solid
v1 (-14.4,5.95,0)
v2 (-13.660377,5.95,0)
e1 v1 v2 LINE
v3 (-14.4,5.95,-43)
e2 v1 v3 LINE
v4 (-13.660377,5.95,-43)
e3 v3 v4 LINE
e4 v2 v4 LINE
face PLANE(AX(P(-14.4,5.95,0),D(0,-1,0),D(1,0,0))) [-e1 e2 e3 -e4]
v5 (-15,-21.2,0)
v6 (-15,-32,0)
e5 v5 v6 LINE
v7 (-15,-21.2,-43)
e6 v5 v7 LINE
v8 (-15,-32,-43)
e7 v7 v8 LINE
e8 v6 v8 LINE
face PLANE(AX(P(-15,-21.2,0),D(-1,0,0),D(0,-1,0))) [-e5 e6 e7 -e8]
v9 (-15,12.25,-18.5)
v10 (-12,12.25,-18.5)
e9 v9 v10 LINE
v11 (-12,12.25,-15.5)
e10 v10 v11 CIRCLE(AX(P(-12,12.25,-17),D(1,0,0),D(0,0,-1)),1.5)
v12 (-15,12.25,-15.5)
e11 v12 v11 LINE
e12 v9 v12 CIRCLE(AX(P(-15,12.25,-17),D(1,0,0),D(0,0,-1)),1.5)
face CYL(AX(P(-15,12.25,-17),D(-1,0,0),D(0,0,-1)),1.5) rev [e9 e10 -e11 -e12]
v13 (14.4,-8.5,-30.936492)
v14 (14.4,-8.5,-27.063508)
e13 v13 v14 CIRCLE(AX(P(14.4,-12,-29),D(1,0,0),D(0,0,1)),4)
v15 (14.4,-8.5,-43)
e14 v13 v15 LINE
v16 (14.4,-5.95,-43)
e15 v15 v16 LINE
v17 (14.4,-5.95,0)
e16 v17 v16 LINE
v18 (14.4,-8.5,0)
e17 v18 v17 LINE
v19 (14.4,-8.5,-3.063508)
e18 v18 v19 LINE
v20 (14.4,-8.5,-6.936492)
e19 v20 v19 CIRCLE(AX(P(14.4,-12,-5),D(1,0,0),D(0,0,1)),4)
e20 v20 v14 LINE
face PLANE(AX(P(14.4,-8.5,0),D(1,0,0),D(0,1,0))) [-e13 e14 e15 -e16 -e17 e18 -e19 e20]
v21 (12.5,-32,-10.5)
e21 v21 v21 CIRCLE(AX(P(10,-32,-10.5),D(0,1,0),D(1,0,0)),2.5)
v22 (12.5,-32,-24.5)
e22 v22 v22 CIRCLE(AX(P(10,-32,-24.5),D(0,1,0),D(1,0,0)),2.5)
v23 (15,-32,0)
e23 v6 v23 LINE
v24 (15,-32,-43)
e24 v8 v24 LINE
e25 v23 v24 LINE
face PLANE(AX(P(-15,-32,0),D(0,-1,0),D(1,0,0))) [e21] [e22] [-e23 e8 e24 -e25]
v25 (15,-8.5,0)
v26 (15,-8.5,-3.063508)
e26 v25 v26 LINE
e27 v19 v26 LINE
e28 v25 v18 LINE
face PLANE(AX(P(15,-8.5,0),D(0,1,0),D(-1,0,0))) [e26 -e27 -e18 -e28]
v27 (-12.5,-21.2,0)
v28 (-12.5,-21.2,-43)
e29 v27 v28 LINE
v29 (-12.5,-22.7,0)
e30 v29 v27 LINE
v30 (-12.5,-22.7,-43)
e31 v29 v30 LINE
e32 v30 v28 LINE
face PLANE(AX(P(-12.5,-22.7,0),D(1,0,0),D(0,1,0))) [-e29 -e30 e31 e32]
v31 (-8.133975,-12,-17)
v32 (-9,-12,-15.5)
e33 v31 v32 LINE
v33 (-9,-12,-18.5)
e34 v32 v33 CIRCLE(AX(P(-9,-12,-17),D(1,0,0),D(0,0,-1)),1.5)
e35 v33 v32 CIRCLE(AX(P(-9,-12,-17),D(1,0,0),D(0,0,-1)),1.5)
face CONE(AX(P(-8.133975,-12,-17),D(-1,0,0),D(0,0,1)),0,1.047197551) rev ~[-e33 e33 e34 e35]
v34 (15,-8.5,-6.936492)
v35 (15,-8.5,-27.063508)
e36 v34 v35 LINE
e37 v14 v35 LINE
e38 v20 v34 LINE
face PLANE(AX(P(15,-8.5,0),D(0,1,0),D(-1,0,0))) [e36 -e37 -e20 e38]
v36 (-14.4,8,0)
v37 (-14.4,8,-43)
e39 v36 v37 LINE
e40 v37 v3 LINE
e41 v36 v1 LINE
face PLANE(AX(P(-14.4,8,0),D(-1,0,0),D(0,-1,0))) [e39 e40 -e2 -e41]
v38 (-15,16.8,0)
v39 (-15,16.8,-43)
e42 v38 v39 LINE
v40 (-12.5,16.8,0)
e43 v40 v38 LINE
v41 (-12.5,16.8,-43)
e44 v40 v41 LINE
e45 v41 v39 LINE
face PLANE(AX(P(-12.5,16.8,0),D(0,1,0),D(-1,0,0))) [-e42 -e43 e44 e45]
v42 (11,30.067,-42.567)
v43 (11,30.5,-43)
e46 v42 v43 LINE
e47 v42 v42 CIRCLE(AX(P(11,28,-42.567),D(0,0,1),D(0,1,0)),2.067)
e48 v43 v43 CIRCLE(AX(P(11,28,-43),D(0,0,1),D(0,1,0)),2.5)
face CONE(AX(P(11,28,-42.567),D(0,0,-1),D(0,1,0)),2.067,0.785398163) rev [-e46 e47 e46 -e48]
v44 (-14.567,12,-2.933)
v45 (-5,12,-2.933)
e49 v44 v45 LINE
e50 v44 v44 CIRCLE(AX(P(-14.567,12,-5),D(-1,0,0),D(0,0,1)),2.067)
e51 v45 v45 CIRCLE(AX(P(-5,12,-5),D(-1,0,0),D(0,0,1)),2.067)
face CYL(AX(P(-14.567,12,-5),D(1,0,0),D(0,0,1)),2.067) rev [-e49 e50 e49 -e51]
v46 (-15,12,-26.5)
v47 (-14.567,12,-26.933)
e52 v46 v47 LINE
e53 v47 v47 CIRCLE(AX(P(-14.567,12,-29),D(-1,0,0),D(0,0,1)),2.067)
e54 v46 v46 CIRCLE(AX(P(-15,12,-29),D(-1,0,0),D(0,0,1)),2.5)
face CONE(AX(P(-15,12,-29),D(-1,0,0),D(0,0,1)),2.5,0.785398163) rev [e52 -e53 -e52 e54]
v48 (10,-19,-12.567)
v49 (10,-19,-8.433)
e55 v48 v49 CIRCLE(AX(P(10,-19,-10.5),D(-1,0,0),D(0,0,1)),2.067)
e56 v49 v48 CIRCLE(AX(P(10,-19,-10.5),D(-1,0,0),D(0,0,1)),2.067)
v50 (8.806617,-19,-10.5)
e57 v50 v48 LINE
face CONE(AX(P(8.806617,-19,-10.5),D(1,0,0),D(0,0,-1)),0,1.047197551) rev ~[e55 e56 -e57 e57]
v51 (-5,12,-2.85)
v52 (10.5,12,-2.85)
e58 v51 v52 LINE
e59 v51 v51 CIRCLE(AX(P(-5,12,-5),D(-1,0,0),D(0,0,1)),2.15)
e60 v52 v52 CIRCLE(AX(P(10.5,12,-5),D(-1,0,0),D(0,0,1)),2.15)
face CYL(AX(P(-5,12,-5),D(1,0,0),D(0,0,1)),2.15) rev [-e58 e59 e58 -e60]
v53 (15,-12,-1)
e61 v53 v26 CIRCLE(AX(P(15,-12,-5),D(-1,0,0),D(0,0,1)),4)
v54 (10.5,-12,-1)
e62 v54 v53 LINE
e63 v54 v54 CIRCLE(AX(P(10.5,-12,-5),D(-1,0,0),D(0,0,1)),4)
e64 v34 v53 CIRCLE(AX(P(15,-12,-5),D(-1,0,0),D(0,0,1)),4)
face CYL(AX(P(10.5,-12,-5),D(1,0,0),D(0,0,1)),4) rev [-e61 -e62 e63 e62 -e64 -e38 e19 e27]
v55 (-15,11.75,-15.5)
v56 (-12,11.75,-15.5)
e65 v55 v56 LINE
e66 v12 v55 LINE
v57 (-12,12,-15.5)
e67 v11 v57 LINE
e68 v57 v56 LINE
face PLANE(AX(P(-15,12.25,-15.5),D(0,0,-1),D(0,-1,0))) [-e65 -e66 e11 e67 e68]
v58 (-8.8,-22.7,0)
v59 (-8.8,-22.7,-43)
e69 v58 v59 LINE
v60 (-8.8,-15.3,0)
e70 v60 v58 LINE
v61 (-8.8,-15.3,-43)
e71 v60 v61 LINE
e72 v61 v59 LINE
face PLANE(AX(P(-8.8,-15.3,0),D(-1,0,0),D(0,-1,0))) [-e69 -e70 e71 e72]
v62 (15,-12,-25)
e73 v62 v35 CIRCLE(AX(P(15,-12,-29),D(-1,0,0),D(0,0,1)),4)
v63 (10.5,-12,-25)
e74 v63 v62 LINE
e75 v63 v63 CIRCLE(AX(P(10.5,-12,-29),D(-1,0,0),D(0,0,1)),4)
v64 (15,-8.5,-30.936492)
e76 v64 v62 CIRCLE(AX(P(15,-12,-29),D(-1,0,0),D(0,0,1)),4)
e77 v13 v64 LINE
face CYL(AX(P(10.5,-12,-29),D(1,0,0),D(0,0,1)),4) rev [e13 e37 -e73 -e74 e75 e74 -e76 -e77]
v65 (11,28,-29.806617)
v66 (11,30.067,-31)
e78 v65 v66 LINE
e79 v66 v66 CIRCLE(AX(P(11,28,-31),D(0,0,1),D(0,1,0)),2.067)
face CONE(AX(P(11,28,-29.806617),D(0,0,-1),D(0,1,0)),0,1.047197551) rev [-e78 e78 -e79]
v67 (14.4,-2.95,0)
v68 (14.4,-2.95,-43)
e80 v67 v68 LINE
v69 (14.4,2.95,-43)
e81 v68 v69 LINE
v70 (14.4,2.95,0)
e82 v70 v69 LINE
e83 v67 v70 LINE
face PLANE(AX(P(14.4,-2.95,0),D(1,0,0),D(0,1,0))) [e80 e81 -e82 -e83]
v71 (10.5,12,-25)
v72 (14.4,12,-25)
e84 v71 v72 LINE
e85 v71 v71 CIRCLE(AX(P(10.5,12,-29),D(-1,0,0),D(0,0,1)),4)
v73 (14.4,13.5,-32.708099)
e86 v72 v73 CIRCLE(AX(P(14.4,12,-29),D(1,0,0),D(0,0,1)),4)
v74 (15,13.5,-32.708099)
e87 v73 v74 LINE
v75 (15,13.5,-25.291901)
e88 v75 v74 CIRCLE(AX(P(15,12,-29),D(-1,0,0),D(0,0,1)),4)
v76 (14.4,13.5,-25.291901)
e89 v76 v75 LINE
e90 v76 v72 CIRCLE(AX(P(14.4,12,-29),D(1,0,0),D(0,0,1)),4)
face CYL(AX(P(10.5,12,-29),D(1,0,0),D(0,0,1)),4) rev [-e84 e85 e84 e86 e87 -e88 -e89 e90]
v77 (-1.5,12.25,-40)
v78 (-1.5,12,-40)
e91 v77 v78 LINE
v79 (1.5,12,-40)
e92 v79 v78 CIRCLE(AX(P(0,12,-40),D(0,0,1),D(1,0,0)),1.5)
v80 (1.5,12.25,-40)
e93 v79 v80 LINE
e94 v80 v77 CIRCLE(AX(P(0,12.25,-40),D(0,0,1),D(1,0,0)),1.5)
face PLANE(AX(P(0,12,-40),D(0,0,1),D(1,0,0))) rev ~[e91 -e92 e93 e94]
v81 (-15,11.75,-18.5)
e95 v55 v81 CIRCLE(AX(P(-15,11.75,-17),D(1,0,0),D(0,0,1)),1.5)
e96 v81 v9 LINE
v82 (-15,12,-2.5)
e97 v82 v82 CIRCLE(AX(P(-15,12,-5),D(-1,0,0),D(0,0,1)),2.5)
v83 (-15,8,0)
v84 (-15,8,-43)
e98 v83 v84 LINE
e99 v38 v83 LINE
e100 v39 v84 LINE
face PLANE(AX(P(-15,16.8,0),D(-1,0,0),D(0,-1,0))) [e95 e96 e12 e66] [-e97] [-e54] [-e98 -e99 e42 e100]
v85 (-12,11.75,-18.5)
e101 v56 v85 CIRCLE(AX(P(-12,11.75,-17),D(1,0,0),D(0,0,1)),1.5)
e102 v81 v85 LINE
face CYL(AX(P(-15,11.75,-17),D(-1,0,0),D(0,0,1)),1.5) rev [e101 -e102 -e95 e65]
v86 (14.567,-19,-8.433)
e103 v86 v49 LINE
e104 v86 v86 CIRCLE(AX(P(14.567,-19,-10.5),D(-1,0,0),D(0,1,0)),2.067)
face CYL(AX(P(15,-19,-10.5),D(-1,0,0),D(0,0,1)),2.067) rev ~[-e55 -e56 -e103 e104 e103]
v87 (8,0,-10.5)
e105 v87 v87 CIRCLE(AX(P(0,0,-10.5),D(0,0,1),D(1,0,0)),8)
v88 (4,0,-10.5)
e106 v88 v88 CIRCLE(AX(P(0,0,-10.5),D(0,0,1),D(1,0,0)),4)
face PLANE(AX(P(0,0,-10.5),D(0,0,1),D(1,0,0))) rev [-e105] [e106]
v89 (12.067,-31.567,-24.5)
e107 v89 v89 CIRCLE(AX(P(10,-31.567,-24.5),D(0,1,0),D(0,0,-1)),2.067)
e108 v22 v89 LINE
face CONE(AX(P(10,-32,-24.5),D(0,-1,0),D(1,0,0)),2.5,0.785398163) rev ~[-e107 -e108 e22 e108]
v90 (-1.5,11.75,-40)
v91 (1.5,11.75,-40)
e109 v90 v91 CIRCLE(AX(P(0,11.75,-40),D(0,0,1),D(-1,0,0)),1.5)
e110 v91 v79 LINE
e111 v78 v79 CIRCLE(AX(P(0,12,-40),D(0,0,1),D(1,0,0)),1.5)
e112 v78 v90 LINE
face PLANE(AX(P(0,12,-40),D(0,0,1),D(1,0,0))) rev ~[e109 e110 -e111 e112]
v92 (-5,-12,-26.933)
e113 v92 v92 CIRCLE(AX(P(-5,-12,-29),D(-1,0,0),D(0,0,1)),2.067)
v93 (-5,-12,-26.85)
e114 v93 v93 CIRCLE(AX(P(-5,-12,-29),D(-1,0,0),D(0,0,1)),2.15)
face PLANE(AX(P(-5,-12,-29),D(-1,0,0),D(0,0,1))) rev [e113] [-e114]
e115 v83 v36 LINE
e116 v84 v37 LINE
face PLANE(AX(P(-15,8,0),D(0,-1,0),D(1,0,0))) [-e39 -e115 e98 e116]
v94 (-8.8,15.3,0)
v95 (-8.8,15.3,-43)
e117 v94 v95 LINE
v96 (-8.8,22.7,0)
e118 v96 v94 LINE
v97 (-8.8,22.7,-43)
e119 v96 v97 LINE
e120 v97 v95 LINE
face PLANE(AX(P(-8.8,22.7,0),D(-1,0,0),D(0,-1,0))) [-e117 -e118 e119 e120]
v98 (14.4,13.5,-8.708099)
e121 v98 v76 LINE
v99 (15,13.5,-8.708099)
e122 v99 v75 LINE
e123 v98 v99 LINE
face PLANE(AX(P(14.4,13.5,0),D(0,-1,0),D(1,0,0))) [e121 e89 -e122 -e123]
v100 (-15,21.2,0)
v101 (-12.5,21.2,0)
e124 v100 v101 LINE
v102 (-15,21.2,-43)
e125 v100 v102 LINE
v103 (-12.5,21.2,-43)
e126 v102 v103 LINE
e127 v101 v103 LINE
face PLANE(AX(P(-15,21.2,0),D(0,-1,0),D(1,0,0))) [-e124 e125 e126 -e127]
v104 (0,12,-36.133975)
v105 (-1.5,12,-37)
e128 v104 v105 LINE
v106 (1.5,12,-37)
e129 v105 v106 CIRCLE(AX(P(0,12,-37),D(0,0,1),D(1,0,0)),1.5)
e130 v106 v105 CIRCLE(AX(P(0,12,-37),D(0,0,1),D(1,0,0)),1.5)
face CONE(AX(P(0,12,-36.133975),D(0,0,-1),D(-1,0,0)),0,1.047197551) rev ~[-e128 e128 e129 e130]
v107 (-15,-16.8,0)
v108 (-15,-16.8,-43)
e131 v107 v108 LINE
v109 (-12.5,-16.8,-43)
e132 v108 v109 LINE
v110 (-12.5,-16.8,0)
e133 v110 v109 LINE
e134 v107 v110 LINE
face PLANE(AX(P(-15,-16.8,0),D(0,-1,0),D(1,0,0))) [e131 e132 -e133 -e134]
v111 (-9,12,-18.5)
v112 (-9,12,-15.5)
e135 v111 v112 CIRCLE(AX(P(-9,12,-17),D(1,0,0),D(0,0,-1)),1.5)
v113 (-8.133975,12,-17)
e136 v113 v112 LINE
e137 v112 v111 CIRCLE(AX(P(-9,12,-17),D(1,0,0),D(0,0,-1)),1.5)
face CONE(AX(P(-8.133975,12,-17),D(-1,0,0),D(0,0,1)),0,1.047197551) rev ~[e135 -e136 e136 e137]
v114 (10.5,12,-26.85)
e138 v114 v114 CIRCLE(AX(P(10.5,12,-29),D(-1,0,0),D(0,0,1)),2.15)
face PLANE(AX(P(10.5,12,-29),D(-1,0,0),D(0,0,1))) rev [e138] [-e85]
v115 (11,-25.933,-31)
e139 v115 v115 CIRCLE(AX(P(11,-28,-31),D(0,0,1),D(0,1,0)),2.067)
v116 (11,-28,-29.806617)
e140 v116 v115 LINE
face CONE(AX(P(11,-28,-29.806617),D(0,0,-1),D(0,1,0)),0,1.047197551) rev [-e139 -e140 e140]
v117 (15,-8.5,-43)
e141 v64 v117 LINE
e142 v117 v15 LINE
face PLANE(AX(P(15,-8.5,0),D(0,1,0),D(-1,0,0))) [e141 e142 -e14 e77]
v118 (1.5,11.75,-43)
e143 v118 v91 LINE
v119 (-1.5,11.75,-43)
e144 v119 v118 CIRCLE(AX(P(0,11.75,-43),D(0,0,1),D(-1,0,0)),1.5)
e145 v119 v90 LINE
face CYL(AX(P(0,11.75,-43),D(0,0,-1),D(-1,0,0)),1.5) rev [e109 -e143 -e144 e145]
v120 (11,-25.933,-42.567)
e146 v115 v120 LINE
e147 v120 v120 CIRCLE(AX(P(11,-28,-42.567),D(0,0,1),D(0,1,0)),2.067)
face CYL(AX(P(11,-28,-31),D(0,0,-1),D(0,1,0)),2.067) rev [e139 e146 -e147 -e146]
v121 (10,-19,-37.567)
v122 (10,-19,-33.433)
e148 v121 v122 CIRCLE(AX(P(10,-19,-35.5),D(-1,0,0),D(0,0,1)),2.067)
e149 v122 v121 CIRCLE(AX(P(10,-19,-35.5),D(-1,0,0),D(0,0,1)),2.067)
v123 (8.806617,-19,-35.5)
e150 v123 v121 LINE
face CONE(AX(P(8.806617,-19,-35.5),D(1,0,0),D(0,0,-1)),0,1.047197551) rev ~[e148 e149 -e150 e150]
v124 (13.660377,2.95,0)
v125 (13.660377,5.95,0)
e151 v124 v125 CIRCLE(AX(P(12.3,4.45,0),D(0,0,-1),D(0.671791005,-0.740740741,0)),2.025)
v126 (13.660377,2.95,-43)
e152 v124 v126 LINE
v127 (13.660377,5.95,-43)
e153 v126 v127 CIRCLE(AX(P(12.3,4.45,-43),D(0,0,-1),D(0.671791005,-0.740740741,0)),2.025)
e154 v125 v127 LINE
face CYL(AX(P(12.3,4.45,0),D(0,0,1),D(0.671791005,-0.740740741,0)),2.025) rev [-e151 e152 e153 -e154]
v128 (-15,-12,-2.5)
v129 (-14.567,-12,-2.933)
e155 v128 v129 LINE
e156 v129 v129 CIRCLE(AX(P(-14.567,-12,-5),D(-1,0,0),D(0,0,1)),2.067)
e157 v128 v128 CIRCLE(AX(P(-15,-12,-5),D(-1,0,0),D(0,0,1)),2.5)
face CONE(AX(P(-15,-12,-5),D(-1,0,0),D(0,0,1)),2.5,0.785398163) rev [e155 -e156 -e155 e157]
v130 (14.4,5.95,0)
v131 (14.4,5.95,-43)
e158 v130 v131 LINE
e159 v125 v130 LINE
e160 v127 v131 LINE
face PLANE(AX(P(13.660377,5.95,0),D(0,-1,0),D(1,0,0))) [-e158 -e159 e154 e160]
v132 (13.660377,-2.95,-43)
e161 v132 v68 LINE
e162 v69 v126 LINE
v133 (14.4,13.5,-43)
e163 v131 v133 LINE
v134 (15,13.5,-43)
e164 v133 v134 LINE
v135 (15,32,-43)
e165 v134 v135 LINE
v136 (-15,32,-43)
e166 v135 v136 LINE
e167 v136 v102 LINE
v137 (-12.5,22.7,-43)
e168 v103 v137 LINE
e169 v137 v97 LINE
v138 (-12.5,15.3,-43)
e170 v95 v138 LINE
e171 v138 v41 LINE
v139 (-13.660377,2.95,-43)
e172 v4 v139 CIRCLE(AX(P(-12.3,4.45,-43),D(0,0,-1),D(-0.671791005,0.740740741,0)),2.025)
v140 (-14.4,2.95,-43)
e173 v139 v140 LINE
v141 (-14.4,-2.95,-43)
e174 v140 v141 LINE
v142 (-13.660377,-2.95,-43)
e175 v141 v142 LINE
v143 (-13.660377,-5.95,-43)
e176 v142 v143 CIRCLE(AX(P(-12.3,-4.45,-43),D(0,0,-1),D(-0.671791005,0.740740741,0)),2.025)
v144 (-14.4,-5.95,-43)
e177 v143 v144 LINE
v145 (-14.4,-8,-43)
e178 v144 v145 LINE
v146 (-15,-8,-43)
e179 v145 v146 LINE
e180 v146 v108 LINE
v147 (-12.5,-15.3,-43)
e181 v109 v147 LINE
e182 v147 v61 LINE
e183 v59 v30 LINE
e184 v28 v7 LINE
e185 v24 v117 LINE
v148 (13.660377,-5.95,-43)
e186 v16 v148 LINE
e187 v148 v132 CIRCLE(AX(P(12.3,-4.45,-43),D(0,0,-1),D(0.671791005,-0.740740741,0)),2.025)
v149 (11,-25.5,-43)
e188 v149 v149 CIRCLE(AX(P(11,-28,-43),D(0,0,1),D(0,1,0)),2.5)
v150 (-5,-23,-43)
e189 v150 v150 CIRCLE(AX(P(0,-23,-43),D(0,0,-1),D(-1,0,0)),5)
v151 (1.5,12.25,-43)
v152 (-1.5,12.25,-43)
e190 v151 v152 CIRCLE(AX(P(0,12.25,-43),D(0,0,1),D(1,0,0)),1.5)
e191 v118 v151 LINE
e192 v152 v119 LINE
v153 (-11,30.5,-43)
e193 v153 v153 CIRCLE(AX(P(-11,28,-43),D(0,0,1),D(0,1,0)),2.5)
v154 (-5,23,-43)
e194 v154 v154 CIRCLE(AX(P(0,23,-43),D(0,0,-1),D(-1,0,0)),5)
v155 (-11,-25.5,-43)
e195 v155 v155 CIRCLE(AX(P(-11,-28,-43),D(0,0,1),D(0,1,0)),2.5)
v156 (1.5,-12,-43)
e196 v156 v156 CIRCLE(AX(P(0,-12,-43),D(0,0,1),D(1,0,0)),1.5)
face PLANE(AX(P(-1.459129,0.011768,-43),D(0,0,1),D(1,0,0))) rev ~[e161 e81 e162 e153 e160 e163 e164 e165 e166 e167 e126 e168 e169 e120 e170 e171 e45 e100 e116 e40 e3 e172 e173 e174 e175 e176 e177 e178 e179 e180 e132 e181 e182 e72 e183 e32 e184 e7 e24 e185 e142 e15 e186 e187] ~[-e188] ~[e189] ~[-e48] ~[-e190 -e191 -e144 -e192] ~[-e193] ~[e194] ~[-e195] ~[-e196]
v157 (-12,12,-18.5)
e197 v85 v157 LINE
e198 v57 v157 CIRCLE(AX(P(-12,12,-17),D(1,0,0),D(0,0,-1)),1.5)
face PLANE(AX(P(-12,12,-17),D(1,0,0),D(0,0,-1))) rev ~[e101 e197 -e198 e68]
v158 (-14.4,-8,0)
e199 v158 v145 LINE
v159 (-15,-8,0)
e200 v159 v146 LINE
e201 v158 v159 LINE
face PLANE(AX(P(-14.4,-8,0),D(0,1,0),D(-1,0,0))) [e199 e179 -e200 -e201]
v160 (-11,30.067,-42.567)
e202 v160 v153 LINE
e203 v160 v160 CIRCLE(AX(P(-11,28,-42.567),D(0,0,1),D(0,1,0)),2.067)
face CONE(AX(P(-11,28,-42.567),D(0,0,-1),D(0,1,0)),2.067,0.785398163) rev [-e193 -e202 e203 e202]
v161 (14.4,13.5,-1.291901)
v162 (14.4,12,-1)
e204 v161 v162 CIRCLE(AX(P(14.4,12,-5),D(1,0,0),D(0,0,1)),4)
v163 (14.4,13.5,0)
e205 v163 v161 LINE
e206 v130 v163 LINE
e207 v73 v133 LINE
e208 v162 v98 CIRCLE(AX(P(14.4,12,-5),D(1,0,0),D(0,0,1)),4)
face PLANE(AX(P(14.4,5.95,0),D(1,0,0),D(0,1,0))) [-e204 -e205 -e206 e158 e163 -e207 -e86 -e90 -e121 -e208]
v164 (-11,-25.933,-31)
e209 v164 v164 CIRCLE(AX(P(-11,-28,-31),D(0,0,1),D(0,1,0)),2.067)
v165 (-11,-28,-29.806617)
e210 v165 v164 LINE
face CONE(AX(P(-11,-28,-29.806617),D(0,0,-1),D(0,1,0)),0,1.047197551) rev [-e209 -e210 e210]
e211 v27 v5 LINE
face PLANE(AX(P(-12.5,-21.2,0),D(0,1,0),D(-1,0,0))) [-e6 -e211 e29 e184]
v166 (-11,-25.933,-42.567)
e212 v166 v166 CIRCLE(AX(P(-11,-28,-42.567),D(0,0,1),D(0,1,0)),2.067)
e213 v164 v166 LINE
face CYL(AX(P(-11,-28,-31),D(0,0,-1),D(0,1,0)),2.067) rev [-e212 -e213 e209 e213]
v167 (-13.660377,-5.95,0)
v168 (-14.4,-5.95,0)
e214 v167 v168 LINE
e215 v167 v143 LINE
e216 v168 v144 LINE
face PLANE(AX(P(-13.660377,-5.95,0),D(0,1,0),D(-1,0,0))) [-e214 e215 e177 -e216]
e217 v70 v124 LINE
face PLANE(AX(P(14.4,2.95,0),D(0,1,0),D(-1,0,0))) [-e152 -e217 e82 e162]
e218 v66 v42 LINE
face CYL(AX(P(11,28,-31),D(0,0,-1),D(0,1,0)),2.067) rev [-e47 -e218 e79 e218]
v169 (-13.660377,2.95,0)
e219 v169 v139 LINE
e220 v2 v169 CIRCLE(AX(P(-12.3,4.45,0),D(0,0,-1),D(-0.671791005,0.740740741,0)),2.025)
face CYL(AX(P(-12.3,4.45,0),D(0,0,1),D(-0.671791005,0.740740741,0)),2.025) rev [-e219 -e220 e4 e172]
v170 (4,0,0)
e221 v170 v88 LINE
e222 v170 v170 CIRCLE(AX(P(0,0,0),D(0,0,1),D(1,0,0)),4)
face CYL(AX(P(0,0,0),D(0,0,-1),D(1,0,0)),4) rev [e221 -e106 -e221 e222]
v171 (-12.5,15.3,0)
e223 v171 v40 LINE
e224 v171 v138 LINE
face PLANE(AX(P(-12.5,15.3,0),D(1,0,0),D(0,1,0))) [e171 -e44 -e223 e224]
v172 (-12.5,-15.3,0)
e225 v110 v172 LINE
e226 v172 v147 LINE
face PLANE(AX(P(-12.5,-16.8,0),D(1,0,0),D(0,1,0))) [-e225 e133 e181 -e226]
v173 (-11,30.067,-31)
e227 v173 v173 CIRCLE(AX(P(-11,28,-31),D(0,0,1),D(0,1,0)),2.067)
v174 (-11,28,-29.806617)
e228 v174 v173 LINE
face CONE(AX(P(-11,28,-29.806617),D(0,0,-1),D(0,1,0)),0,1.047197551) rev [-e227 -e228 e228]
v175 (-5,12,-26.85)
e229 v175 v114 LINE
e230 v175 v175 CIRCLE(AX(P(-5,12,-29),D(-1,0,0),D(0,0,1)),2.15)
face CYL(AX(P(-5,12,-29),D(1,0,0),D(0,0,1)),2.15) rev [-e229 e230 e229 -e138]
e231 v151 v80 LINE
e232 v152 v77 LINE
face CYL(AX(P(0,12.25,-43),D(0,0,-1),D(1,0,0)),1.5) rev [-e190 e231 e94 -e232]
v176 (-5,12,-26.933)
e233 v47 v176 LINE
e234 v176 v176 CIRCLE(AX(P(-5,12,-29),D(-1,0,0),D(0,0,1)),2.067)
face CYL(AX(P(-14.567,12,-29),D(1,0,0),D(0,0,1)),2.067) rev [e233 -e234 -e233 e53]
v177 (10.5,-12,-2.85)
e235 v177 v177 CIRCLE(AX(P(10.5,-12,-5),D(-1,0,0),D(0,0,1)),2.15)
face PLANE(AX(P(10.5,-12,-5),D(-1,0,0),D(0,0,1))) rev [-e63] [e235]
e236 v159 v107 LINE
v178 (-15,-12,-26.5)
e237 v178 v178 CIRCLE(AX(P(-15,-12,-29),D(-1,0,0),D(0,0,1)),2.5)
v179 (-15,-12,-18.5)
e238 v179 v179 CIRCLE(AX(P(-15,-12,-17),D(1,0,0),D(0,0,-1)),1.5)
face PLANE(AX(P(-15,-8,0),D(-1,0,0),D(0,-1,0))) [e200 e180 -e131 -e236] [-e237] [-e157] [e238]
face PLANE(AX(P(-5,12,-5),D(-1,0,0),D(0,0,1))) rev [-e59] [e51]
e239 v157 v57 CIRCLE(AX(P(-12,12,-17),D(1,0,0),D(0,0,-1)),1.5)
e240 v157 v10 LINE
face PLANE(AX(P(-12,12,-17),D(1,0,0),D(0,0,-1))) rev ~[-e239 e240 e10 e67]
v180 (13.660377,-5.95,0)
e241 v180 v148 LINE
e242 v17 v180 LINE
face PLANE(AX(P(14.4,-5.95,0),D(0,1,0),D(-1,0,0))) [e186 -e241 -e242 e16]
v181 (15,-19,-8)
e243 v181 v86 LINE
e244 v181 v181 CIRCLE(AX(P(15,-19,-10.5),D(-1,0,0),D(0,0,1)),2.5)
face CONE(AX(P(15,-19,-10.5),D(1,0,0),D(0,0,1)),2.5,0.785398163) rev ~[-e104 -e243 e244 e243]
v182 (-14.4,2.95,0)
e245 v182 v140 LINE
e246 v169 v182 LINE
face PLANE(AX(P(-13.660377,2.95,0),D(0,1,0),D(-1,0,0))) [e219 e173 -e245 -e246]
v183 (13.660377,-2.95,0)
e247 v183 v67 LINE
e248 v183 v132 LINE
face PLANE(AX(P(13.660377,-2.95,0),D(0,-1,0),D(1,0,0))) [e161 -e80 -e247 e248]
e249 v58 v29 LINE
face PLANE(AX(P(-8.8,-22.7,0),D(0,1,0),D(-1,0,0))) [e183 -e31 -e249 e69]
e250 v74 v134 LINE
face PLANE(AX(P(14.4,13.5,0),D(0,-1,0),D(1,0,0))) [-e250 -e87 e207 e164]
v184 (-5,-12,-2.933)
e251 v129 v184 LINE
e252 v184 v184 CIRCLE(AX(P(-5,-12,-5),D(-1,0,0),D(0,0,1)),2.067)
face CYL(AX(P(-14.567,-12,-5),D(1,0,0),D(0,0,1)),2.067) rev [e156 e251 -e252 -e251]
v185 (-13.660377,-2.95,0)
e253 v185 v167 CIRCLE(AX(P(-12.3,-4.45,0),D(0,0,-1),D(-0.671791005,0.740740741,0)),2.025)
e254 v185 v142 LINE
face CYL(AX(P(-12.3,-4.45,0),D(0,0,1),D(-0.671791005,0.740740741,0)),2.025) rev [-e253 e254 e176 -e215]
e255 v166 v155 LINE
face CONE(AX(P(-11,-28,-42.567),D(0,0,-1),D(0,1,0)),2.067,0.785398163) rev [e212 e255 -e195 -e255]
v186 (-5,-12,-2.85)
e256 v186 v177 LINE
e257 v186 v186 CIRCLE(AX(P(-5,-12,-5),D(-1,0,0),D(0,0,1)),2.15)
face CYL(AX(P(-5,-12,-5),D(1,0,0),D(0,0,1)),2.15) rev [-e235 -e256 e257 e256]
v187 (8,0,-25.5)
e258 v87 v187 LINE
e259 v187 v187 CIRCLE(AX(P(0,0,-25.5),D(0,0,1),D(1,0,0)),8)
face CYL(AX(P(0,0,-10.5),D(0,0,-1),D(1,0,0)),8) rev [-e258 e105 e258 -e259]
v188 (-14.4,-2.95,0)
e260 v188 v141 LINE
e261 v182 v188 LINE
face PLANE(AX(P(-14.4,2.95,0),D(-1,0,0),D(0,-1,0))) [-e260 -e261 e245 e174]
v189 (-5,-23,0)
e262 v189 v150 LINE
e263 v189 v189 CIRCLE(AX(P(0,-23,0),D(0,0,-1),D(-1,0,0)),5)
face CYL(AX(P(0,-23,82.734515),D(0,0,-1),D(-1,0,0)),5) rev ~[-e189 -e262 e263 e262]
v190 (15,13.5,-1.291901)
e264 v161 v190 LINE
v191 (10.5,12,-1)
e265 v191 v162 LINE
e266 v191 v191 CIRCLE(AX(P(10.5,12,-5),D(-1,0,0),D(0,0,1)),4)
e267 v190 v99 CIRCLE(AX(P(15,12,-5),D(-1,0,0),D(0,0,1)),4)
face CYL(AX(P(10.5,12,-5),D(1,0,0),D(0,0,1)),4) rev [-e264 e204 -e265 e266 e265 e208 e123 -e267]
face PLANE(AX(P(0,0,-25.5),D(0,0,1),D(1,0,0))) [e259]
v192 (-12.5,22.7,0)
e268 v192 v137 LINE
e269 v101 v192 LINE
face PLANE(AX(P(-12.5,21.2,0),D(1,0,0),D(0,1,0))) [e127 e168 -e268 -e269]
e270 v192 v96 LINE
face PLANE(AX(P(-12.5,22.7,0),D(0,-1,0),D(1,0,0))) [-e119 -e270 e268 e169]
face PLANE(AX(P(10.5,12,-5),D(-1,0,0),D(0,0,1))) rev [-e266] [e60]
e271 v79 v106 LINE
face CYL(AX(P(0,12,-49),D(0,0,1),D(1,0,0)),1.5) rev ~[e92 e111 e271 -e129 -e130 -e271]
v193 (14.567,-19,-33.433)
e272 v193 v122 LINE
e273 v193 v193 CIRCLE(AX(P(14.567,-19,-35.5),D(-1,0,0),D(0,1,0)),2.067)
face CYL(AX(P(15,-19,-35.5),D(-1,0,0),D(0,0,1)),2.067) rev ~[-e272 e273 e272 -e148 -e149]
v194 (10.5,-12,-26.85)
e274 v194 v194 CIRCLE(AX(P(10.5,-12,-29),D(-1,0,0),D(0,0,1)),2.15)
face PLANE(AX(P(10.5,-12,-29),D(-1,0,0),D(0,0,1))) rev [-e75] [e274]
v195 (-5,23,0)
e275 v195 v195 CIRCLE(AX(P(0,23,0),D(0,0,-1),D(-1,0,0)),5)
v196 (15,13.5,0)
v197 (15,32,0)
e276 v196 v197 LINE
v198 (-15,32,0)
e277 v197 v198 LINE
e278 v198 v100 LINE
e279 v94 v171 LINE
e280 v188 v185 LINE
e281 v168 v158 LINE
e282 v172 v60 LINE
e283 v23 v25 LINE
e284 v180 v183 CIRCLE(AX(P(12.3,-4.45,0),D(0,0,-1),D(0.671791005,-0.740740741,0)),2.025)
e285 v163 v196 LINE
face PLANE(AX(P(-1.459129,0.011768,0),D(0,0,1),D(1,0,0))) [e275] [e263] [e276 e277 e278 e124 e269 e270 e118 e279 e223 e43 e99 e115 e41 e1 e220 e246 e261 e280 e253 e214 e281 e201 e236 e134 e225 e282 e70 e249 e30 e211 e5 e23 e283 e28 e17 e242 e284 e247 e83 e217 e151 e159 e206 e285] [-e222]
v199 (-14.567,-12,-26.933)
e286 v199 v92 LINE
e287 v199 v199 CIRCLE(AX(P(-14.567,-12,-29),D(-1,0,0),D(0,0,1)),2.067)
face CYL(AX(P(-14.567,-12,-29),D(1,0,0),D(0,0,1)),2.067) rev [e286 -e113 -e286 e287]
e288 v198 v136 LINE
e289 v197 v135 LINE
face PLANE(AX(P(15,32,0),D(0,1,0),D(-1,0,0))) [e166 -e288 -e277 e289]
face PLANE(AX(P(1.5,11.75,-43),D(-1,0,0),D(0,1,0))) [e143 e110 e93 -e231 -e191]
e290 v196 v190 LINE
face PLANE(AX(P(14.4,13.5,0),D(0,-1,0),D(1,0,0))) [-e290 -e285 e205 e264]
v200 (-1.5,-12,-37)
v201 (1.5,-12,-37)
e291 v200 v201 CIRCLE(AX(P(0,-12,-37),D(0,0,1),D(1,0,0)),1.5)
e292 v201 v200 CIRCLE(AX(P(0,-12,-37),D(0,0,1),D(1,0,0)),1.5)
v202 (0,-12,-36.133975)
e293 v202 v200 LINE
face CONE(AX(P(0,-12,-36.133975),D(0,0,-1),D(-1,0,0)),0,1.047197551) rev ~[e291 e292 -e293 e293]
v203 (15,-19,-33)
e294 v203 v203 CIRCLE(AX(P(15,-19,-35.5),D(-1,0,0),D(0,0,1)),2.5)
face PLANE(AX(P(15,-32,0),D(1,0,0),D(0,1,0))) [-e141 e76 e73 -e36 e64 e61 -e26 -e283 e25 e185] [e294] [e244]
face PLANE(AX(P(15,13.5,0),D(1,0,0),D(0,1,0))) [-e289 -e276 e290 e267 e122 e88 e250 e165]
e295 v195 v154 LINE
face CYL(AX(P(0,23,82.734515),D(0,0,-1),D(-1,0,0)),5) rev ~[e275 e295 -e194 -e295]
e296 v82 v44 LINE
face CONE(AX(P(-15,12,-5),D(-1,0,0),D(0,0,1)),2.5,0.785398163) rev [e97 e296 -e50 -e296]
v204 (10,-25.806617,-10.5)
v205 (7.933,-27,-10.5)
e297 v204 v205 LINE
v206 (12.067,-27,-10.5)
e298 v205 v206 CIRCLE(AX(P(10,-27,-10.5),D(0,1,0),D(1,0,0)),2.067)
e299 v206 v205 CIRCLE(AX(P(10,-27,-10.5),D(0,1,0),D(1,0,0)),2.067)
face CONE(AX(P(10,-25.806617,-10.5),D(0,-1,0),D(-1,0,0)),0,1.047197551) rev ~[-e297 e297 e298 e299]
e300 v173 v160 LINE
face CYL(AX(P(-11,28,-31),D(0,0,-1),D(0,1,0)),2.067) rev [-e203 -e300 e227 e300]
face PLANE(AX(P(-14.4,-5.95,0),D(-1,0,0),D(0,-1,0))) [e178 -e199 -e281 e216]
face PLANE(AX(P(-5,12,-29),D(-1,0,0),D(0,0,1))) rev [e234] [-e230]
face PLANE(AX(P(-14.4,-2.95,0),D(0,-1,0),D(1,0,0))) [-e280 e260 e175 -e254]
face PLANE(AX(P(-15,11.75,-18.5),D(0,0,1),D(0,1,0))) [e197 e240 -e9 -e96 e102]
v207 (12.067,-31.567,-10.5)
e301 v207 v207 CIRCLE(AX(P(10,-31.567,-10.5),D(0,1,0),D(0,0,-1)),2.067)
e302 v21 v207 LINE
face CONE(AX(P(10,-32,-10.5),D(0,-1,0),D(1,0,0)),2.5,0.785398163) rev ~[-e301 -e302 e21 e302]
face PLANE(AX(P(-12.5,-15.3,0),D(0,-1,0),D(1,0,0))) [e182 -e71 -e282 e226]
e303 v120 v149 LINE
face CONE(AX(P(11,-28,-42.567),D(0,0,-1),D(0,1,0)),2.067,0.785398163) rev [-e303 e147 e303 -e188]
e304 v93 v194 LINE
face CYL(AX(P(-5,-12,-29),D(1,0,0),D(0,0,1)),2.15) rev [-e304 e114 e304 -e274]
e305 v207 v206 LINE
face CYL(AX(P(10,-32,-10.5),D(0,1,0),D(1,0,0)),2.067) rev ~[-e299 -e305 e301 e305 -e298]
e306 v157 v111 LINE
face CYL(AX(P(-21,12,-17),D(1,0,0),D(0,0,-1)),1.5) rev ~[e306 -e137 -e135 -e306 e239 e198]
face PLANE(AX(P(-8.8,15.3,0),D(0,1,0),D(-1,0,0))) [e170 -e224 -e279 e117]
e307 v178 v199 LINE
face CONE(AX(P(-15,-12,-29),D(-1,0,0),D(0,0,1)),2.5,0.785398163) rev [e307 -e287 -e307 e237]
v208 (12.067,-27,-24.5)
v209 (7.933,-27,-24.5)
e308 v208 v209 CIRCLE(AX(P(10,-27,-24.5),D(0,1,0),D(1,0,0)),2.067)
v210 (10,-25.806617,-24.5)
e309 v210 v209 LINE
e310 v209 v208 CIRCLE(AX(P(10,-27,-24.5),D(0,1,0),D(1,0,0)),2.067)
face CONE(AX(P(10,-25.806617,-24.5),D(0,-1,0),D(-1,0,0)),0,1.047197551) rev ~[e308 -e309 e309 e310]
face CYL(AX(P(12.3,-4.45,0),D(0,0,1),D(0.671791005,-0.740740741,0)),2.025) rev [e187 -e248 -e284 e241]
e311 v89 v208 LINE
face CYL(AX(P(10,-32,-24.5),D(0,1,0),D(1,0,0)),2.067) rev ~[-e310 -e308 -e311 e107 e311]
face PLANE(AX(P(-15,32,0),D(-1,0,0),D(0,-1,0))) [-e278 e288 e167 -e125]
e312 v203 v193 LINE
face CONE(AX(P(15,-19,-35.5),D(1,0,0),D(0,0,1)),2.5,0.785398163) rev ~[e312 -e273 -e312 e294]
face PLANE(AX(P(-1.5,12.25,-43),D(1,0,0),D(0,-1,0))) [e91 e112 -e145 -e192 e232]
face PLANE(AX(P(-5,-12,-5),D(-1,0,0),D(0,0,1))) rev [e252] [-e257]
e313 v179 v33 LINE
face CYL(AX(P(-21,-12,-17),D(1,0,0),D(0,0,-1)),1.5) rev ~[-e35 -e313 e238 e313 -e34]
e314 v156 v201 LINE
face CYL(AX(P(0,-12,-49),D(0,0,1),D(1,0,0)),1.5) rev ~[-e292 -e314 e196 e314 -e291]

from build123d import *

# Parameters (mm, degrees)
BOSS_EXTRUDE1_DEPTH  = 43
HOLE1_D              = 4.134
HOLE1_DEPTH          = 5
HOLE1_CSINK_D        = 5
HOLE1_CSINK_ANGLE    = 90
HOLE1_TIP            = 1.193383006
HOLE2_D              = 4.134
HOLE2_DEPTH          = 5
HOLE2_CSINK_D        = 5
HOLE2_CSINK_ANGLE    = 90
HOLE2_TIP            = 1.193383006
HOLE3_D              = 4.134
HOLE3_DEPTH          = 5
HOLE3_CSINK_D        = 5
HOLE3_CSINK_ANGLE    = 90
HOLE3_TIP            = 1.193383006
HOLE4_D              = 4.134
HOLE4_DEPTH          = 5
HOLE4_CSINK_D        = 5
HOLE4_CSINK_ANGLE    = 90
HOLE4_TIP            = 1.193383006
HOLE5_D              = 3
HOLE5_DEPTH          = 6
HOLE5_TIP            = 0.866025404
CUT_EXTRUDE1_DEPTH   = 3
HOLE6_D              = 3
HOLE6_DEPTH          = 6
HOLE6_TIP            = 0.866025404
HOLE7_D              = 10
HOLE8_D              = 10
HOLE9_D              = 3
HOLE9_DEPTH          = 6
HOLE9_TIP            = 0.866025404
CUT_EXTRUDE2_DEPTH   = 3
HOLE10_D             = 3
HOLE10_DEPTH         = 6
HOLE10_TIP           = 0.866025404
LPATTERN1_COUNT      = 2
LPATTERN1_PITCH      = 22
LPATTERN1_COUNT_DIR2 = 2
LPATTERN1_PITCH_DIR2 = 56


with BuildPart() as part:
    # Sketch1 → Boss-Extrude1 (new body)
    with BuildSketch(Plane.XY):
        with BuildLine():
            Line((-15, 32), (-15, 21.2))
            Line((-15, 21.2), (-12.5, 21.2))
            Line((-12.5, 21.2), (-12.5, 22.7))
            Line((-12.5, 22.7), (-8.8, 22.7))
            Line((-8.8, 22.7), (-8.8, 15.3))
            Line((-8.8, 15.3), (-12.5, 15.3))
            Line((-12.5, 15.3), (-12.5, 16.8))
            Line((-12.5, 16.8), (-15, 16.8))
            Line((-15, 16.8), (-15, 8))
            Line((-15, 8), (-14.4, 8))
            Line((-14.4, 8), (-14.4, 5.95))
            Line((-14.4, 5.95), (-13.660376786, 5.95))
            ThreePointArc((-13.660376786, 5.95), (-10.275, 4.45), (-13.660376786, 2.95))
            Line((-13.660376786, 2.95), (-14.4, 2.95))
            Line((-14.4, 2.95), (-14.4, -2.95))
            Line((-14.4, -2.95), (-13.660376786, -2.95))
            ThreePointArc((-13.660376786, -2.95), (-10.275, -4.45), (-13.660376786, -5.95))
            Line((-13.660376786, -5.95), (-14.4, -5.95))
            Line((-14.4, -5.95), (-14.4, -8))
            Line((-14.4, -8), (-15, -8))
            Line((-15, -8), (-15, -16.8))
            Line((-15, -16.8), (-12.5, -16.8))
            Line((-12.5, -16.8), (-12.5, -15.3))
            Line((-12.5, -15.3), (-8.8, -15.3))
            Line((-8.8, -15.3), (-8.8, -22.7))
            Line((-8.8, -22.7), (-12.5, -22.7))
            Line((-12.5, -22.7), (-12.5, -21.2))
            Line((-12.5, -21.2), (-15, -21.2))
            Line((-15, -21.2), (-15, -32))
            Line((-15, -32), (15, -32))
            Line((15, -32), (15, -8.5))
            Line((15, -8.5), (14.4, -8.5))
            Line((14.4, -8.5), (14.4, -5.95))
            Line((14.4, -5.95), (13.660376786, -5.95))
            ThreePointArc((13.660376786, -5.95), (10.275, -4.45), (13.660376786, -2.95))
            Line((13.660376786, -2.95), (14.4, -2.95))
            Line((14.4, -2.95), (14.4, 2.95))
            Line((14.4, 2.95), (13.660376786, 2.95))
            ThreePointArc((13.660376786, 2.95), (10.275, 4.45), (13.660376786, 5.95))
            Line((13.660376786, 5.95), (14.4, 5.95))
            Line((14.4, 5.95), (14.4, 13.5))
            Line((14.4, 13.5), (15, 13.5))
            Line((15, 13.5), (15, 32))
            Line((15, 32), (-15, 32))
        make_face()
    extrude(amount=-BOSS_EXTRUDE1_DEPTH)

    # Sketch2 → Cut-Revolve1 (revolve, cut)
    with BuildSketch(Plane(origin=(0, 0, 0), x_dir=(0, 0, -1), z_dir=(1, 0, 0)), mode=Mode.PRIVATE) as cut_revolve1_sk:
        Polygon((0, 0), (0, 4), (10.5, 4), (10.5, 8), (25.5, 8), (25.5, 0), align=None)
    revolve(cut_revolve1_sk.sketch.rotate(Axis((0, 0, -25.5), (0, 0, 1)), 270), axis=Axis((0, 0, -25.5), (0, 0, 1)), mode=Mode.SUBTRACT)

    # Hole1
    with Locations(Plane(origin=(15, 0, 0), x_dir=(0, 0, -1), z_dir=(1, 0, 0))):
        with Locations((10.5, -19)):
            CounterSinkHole(HOLE1_D / 2, HOLE1_CSINK_D / 2, depth=HOLE1_DEPTH, counter_sink_angle=HOLE1_CSINK_ANGLE)
            with Locations((0, 0, -(HOLE1_DEPTH + HOLE1_TIP / 2))):  # 120° drill point
                Cone(0, HOLE1_D / 2, HOLE1_TIP, mode=Mode.SUBTRACT)

    # Hole2
    with Locations(Plane(origin=(15, 0, 0), x_dir=(0, 0, -1), z_dir=(1, 0, 0))):
        with Locations((35.5, -19)):
            CounterSinkHole(HOLE2_D / 2, HOLE2_CSINK_D / 2, depth=HOLE2_DEPTH, counter_sink_angle=HOLE2_CSINK_ANGLE)
            with Locations((0, 0, -(HOLE2_DEPTH + HOLE2_TIP / 2))):  # 120° drill point
                Cone(0, HOLE2_D / 2, HOLE2_TIP, mode=Mode.SUBTRACT)

    # Sketch7 → Cut-Revolve2 (revolve, cut)
    with BuildSketch(Plane(origin=(0, -12, 0), x_dir=(1, 0, 0), z_dir=(0, 1, 0)), mode=Mode.PRIVATE) as cut_revolve2_sk:
        Polygon((-15, 5), (-15, 7.5), (-14.567, 7.067), (-5, 7.067), (-5, 7.15), (10.5, 7.15), (10.5, 9), (15, 9), (15, 5), align=None)
    revolve(cut_revolve2_sk.sketch.rotate(Axis((15, -12, -5), (-1, 0, 0)), 180), axis=Axis((15, -12, -5), (-1, 0, 0)), mode=Mode.SUBTRACT)

    # Sketch8 → Cut-Revolve3 (revolve, cut)
    with BuildSketch(Plane(origin=(0, -12, 0), x_dir=(1, 0, 0), z_dir=(0, 1, 0)), mode=Mode.PRIVATE) as cut_revolve3_sk:
        Polygon((-15, 29), (-15, 31.5), (-14.567, 31.067), (-5, 31.067), (-5, 31.15), (10.5, 31.15), (10.5, 33), (15, 33), (15, 29), align=None)
    revolve(cut_revolve3_sk.sketch.rotate(Axis((15, -12, -29), (-1, 0, 0)), 180), axis=Axis((15, -12, -29), (-1, 0, 0)), mode=Mode.SUBTRACT)

    # Sketch9 → Cut-Revolve4 (revolve, cut)
    with BuildSketch(Plane(origin=(0, 12, 0), x_dir=(1, 0, 0), z_dir=(0, 1, 0)), mode=Mode.PRIVATE) as cut_revolve4_sk:
        Polygon((-15, 5), (-15, 7.5), (-14.567, 7.067), (-5, 7.067), (-5, 7.15), (10.5, 7.15), (10.5, 9), (15, 9), (15, 5), align=None)
    revolve(cut_revolve4_sk.sketch.rotate(Axis((15, 12, -5), (-1, 0, 0)), 180), axis=Axis((15, 12, -5), (-1, 0, 0)), mode=Mode.SUBTRACT)

    # Sketch10 → Cut-Revolve5 (revolve, cut)
    with BuildSketch(Plane(origin=(0, 12, 0), x_dir=(1, 0, 0), z_dir=(0, 1, 0)), mode=Mode.PRIVATE) as cut_revolve5_sk:
        Polygon((-15, 29), (-15, 31.5), (-14.567, 31.067), (-5, 31.067), (-5, 31.15), (10.5, 31.15), (10.5, 33), (15, 33), (15, 29), align=None)
    revolve(cut_revolve5_sk.sketch.rotate(Axis((15, 12, -29), (-1, 0, 0)), 180), axis=Axis((15, 12, -29), (-1, 0, 0)), mode=Mode.SUBTRACT)

    # Hole3
    with Locations(Plane(origin=(0, -32, 0), x_dir=(-1, 0, 0), z_dir=(0, -1, 0))):
        with Locations((-10, 10.5)):
            CounterSinkHole(HOLE3_D / 2, HOLE3_CSINK_D / 2, depth=HOLE3_DEPTH, counter_sink_angle=HOLE3_CSINK_ANGLE)
            with Locations((0, 0, -(HOLE3_DEPTH + HOLE3_TIP / 2))):  # 120° drill point
                Cone(0, HOLE3_D / 2, HOLE3_TIP, mode=Mode.SUBTRACT)

    # Hole4
    with Locations(Plane(origin=(0, -32, 0), x_dir=(-1, 0, 0), z_dir=(0, -1, 0))):
        with Locations((-10, 24.5)):
            CounterSinkHole(HOLE4_D / 2, HOLE4_CSINK_D / 2, depth=HOLE4_DEPTH, counter_sink_angle=HOLE4_CSINK_ANGLE)
            with Locations((0, 0, -(HOLE4_DEPTH + HOLE4_TIP / 2))):  # 120° drill point
                Cone(0, HOLE4_D / 2, HOLE4_TIP, mode=Mode.SUBTRACT)

    # Hole5
    with Locations(Plane.ZY.offset(15)):
        with Locations((-17, 12)):
            Hole(HOLE5_D / 2, depth=HOLE5_DEPTH)
            with Locations((0, 0, -(HOLE5_DEPTH + HOLE5_TIP / 2))):  # 120° drill point
                Cone(0, HOLE5_D / 2, HOLE5_TIP, mode=Mode.SUBTRACT)

    # Sketch17 → Cut-Extrude1 (cut)
    with BuildSketch(Plane(origin=(-15, 0, 0), x_dir=(0, 0, -1), z_dir=(1, 0, 0))):
        with BuildLine():
            Line((18.5, 11.75), (18.5, 12.25))
            ThreePointArc((18.5, 12.25), (17, 13.75), (15.5, 12.25))
            Line((15.5, 12.25), (15.5, 11.75))
            ThreePointArc((15.5, 11.75), (17, 10.25), (18.5, 11.75))
        make_face()
    extrude(amount=CUT_EXTRUDE1_DEPTH, mode=Mode.SUBTRACT)

    # Hole6
    with Locations(Plane.ZY.offset(15)):
        with Locations((-17, -12)):
            Hole(HOLE6_D / 2, depth=HOLE6_DEPTH)
            with Locations((0, 0, -(HOLE6_DEPTH + HOLE6_TIP / 2))):  # 120° drill point
                Cone(0, HOLE6_D / 2, HOLE6_TIP, mode=Mode.SUBTRACT)

    # Hole7 (through all)
    with Locations(Plane.XY):
        with Locations((0, 23)):
            Hole(HOLE7_D / 2)

    # Hole8 (through all)
    with Locations(Plane.XY):
        with Locations((0, -23)):
            Hole(HOLE8_D / 2)

    # Hole9
    with Locations(Plane(origin=(0, 0, -43), x_dir=(-1, 0, 0), z_dir=(0, 0, -1))):
        with Locations((0, 12)):
            Hole(HOLE9_D / 2, depth=HOLE9_DEPTH)
            with Locations((0, 0, -(HOLE9_DEPTH + HOLE9_TIP / 2))):  # 120° drill point
                Cone(0, HOLE9_D / 2, HOLE9_TIP, mode=Mode.SUBTRACT)

    # Sketch26 → Cut-Extrude2 (cut)
    with BuildSketch(Plane.XY.offset(-43)):
        with BuildLine():
            Line((1.5, 11.75), (1.5, 12.25))
            ThreePointArc((1.5, 12.25), (0, 13.75), (-1.5, 12.25))
            Line((-1.5, 12.25), (-1.5, 11.75))
            ThreePointArc((-1.5, 11.75), (0, 10.25), (1.5, 11.75))
        make_face()
    extrude(amount=CUT_EXTRUDE2_DEPTH, mode=Mode.SUBTRACT)

    # Hole10
    with Locations(Plane(origin=(0, 0, -43), x_dir=(-1, 0, 0), z_dir=(0, 0, -1))):
        with Locations((0, -12)):
            Hole(HOLE10_D / 2, depth=HOLE10_DEPTH)
            with Locations((0, 0, -(HOLE10_DEPTH + HOLE10_TIP / 2))):  # 120° drill point
                Cone(0, HOLE10_D / 2, HOLE10_TIP, mode=Mode.SUBTRACT)

    # Sketch29 → Hole11 (revolve, cut)
    with BuildSketch(Plane(origin=(11, 28, -43), x_dir=(0, 1, 0), z_dir=(1, 0, 0))):
        Polygon((0, 0), (0, 13.193383006), (2.067, 12), (2.067, 0.433), (2.5, 0), align=None)
    hole11 = revolve(axis=Axis((11, 28, -57.308894879), (0, 0, 1)), mode=Mode.SUBTRACT)

    # LPattern1: Hole11 2 × 2
    with Locations(*[(-i * LPATTERN1_PITCH, -j * LPATTERN1_PITCH_DIR2, 0) for i in range(LPATTERN1_COUNT) for j in range(LPATTERN1_COUNT_DIR2) if (i, j) != (0, 0)]):
        add(hole11, mode=Mode.SUBTRACT)


solid = part.part
